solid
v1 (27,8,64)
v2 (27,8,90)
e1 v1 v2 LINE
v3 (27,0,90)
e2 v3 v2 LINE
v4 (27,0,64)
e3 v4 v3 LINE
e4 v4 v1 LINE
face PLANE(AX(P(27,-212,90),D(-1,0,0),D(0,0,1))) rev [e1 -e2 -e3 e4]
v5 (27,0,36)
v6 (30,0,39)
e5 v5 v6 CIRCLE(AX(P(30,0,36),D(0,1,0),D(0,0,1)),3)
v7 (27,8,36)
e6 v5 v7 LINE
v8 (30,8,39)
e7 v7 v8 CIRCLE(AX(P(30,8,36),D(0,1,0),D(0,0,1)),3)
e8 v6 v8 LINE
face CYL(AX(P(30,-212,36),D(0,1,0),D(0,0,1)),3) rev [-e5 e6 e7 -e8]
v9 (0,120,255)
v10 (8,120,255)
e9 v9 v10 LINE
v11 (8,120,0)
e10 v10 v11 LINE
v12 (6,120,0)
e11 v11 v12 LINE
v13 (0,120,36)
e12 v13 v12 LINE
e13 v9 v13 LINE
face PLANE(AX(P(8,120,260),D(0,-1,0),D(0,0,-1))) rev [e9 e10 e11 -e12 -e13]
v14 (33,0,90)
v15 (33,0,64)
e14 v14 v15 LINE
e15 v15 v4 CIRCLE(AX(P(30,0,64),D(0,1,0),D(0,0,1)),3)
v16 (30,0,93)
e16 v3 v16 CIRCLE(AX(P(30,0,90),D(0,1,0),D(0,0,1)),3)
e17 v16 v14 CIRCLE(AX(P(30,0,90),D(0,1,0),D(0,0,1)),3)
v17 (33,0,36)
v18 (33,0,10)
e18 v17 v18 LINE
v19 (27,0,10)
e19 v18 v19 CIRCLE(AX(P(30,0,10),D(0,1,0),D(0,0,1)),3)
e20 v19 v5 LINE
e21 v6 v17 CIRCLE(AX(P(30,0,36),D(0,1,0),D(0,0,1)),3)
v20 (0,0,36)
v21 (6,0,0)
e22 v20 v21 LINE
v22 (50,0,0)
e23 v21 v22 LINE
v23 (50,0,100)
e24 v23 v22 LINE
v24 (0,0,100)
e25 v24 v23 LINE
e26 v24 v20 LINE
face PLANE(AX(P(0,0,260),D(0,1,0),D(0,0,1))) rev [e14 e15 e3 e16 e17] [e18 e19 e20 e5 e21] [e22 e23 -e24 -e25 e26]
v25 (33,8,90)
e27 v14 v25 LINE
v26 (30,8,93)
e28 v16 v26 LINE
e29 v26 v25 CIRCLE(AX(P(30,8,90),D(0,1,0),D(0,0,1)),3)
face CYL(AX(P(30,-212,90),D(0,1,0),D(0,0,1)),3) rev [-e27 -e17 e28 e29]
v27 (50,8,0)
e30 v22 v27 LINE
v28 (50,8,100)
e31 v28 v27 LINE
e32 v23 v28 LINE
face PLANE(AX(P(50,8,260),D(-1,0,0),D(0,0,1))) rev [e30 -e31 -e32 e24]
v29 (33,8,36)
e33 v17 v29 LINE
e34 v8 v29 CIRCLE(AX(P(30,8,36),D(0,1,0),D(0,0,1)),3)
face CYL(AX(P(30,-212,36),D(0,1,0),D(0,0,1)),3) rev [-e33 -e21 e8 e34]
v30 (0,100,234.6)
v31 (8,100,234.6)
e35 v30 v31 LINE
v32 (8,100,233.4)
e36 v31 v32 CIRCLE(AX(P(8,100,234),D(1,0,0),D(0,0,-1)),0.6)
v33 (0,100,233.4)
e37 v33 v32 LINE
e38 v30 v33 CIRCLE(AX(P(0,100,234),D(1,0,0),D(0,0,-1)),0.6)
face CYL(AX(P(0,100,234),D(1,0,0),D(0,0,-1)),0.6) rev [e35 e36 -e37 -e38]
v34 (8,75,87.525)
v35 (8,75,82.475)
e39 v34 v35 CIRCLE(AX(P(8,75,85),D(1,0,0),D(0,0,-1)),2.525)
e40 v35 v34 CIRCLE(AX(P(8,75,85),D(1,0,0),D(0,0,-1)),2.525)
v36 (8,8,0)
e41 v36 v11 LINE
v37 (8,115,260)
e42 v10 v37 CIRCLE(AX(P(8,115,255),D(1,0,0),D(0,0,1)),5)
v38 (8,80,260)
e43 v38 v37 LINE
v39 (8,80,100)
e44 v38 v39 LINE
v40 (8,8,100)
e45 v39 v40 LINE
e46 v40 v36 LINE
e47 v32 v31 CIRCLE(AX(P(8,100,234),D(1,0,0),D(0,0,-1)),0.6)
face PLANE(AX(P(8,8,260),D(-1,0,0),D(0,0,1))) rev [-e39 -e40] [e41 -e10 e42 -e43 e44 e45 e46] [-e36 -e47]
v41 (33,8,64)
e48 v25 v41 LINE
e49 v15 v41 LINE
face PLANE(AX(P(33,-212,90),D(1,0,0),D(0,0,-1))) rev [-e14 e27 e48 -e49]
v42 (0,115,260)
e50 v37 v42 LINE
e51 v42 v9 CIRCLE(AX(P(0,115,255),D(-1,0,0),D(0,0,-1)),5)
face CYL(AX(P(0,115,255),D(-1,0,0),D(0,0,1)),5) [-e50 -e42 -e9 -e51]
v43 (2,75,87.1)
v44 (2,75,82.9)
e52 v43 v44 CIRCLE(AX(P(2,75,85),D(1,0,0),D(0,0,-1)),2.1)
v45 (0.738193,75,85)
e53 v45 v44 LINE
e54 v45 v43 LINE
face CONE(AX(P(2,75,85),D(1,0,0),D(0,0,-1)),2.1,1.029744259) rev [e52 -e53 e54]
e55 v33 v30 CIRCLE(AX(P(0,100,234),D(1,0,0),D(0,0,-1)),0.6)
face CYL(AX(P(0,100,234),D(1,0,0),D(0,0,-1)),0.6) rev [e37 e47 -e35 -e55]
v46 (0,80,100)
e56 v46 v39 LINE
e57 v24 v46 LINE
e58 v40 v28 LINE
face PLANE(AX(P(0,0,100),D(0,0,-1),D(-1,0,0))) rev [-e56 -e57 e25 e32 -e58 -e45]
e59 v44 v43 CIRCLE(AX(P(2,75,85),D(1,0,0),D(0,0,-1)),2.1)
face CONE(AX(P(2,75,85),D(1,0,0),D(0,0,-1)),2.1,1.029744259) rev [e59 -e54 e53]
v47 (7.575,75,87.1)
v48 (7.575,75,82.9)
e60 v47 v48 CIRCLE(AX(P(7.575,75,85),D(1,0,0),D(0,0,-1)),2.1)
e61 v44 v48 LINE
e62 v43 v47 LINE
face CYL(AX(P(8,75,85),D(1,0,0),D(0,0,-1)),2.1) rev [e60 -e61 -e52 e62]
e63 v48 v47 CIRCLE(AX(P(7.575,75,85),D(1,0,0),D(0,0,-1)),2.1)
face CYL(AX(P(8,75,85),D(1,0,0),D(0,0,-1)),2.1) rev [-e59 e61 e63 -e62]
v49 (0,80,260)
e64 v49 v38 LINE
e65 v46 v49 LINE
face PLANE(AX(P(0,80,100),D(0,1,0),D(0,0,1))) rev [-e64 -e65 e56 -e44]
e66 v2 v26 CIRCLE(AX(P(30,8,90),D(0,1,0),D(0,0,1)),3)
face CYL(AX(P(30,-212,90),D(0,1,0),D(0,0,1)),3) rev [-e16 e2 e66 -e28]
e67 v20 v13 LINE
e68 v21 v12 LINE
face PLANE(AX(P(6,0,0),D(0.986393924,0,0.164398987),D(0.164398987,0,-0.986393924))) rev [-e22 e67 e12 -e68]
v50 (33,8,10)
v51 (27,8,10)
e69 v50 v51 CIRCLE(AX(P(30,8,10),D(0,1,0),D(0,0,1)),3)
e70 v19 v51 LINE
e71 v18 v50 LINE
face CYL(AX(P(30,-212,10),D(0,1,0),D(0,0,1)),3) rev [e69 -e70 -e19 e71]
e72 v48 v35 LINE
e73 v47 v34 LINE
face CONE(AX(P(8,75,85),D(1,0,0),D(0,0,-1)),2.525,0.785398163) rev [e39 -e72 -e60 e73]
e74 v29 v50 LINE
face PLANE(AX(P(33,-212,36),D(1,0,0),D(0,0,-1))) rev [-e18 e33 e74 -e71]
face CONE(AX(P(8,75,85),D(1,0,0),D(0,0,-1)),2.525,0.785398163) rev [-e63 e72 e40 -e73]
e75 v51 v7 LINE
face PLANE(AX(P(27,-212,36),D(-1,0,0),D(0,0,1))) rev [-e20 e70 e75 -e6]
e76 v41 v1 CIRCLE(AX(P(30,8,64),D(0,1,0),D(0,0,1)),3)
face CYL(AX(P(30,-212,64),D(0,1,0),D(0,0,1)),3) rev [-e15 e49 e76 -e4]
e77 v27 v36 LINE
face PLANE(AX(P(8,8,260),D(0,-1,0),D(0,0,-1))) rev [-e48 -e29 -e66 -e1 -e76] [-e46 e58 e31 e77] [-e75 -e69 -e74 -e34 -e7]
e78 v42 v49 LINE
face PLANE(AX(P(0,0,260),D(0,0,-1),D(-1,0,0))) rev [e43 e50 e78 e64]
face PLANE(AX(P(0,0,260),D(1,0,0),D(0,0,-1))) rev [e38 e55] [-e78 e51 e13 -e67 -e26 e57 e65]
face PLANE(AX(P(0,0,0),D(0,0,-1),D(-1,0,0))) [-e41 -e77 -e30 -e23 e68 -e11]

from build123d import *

# Parameters (mm, degrees)
BOSS_EXTRUDE1_DEPTH         = 260
SKETCH2_W                   = 160
SKETCH2_H                   = 80
CUT_EXTRUDE1_DEPTH          = 291.688837075
CUT_EXTRUDE2_DEPTH          = 220
CUT_EXTRUDE3_DEPTH          = 291.688837075
M5_TAPPED_HOLE1_D           = 4.2
M5_TAPPED_HOLE1_DEPTH       = 6
M5_TAPPED_HOLE1_CSINK_D     = 5.05
M5_TAPPED_HOLE1_CSINK_ANGLE = 90
M5_TAPPED_HOLE1_TIP         = 1.2618073
FILLET1_R                   = 5
SKETCH6_R                   = 0.6
CUT_EXTRUDE4_DEPTH          = 290.420109875


with BuildPart() as part:
    # Sketch1 → Boss-Extrude1 (new body)
    with BuildSketch(Plane.XY):
        Polygon((0, 0), (0, 120), (8, 120), (8, 8), (50, 8), (50, 0), align=None)
    extrude(amount=BOSS_EXTRUDE1_DEPTH)

    # Sketch2 → Cut-Extrude1 (cut, through all)
    with BuildSketch(Plane(origin=(50, 0, 0), x_dir=(0, 0, -1), z_dir=(1, 0, 0))):
        with Locations((-180, 40)):
            Rectangle(SKETCH2_W, SKETCH2_H)
    extrude(amount=-CUT_EXTRUDE1_DEPTH, mode=Mode.SUBTRACT)

    # Sketch3 → Cut-Extrude2 (cut)
    with BuildSketch(Plane(origin=(0, 8, 0), x_dir=(1, 0, 0), z_dir=(0, 1, 0))):
        with BuildLine():
            Line((27, -90), (27, -64))
            ThreePointArc((27, -64), (30, -61), (33, -64))
            Line((33, -64), (33, -90))
            ThreePointArc((33, -90), (30, -93), (27, -90))
        make_face()
        with BuildLine():
            Line((27, -36), (27, -10))
            ThreePointArc((27, -10), (30, -7), (33, -10))
            Line((33, -10), (33, -36))
            ThreePointArc((33, -36), (30, -39), (27, -36))
        make_face()
    extrude(amount=-CUT_EXTRUDE2_DEPTH, mode=Mode.SUBTRACT)

    # Sketch4 → Cut-Extrude3 (cut, through all)
    with BuildSketch(Plane(origin=(0, 120, 0), x_dir=(1, 0, 0), z_dir=(0, 1, 0))):
        Polygon((6, 0), (0, -36), (0, 0), align=None)
    extrude(amount=-CUT_EXTRUDE3_DEPTH, mode=Mode.SUBTRACT)

    # M5 Tapped Hole1
    with Locations(Plane(origin=(8, 75, 85), x_dir=(0, 0, 1), z_dir=(1, 0, 0))):
        with Locations((0, 0)):
            CounterSinkHole(M5_TAPPED_HOLE1_D / 2, M5_TAPPED_HOLE1_CSINK_D / 2, depth=M5_TAPPED_HOLE1_DEPTH, counter_sink_angle=M5_TAPPED_HOLE1_CSINK_ANGLE)
            with Locations((0, 0, -(M5_TAPPED_HOLE1_DEPTH + M5_TAPPED_HOLE1_TIP / 2))):  # 118° drill point
                Cone(0, M5_TAPPED_HOLE1_D / 2, M5_TAPPED_HOLE1_TIP, mode=Mode.SUBTRACT)

    # Fillet1
    fillet1_edges = [part.edges().sort_by_distance(p)[0] for p in [
        (4, 120, 260),
    ]]
    fillet(fillet1_edges, radius=FILLET1_R)

    # Sketch6 → Cut-Extrude4 (cut, through all)
    with BuildSketch(Plane(origin=(8, 0, 0), x_dir=(0, 0, -1), z_dir=(1, 0, 0))):
        with Locations((-234, 100)):
            Circle(SKETCH6_R)
    extrude(amount=-CUT_EXTRUDE4_DEPTH, mode=Mode.SUBTRACT)


solid = part.part
